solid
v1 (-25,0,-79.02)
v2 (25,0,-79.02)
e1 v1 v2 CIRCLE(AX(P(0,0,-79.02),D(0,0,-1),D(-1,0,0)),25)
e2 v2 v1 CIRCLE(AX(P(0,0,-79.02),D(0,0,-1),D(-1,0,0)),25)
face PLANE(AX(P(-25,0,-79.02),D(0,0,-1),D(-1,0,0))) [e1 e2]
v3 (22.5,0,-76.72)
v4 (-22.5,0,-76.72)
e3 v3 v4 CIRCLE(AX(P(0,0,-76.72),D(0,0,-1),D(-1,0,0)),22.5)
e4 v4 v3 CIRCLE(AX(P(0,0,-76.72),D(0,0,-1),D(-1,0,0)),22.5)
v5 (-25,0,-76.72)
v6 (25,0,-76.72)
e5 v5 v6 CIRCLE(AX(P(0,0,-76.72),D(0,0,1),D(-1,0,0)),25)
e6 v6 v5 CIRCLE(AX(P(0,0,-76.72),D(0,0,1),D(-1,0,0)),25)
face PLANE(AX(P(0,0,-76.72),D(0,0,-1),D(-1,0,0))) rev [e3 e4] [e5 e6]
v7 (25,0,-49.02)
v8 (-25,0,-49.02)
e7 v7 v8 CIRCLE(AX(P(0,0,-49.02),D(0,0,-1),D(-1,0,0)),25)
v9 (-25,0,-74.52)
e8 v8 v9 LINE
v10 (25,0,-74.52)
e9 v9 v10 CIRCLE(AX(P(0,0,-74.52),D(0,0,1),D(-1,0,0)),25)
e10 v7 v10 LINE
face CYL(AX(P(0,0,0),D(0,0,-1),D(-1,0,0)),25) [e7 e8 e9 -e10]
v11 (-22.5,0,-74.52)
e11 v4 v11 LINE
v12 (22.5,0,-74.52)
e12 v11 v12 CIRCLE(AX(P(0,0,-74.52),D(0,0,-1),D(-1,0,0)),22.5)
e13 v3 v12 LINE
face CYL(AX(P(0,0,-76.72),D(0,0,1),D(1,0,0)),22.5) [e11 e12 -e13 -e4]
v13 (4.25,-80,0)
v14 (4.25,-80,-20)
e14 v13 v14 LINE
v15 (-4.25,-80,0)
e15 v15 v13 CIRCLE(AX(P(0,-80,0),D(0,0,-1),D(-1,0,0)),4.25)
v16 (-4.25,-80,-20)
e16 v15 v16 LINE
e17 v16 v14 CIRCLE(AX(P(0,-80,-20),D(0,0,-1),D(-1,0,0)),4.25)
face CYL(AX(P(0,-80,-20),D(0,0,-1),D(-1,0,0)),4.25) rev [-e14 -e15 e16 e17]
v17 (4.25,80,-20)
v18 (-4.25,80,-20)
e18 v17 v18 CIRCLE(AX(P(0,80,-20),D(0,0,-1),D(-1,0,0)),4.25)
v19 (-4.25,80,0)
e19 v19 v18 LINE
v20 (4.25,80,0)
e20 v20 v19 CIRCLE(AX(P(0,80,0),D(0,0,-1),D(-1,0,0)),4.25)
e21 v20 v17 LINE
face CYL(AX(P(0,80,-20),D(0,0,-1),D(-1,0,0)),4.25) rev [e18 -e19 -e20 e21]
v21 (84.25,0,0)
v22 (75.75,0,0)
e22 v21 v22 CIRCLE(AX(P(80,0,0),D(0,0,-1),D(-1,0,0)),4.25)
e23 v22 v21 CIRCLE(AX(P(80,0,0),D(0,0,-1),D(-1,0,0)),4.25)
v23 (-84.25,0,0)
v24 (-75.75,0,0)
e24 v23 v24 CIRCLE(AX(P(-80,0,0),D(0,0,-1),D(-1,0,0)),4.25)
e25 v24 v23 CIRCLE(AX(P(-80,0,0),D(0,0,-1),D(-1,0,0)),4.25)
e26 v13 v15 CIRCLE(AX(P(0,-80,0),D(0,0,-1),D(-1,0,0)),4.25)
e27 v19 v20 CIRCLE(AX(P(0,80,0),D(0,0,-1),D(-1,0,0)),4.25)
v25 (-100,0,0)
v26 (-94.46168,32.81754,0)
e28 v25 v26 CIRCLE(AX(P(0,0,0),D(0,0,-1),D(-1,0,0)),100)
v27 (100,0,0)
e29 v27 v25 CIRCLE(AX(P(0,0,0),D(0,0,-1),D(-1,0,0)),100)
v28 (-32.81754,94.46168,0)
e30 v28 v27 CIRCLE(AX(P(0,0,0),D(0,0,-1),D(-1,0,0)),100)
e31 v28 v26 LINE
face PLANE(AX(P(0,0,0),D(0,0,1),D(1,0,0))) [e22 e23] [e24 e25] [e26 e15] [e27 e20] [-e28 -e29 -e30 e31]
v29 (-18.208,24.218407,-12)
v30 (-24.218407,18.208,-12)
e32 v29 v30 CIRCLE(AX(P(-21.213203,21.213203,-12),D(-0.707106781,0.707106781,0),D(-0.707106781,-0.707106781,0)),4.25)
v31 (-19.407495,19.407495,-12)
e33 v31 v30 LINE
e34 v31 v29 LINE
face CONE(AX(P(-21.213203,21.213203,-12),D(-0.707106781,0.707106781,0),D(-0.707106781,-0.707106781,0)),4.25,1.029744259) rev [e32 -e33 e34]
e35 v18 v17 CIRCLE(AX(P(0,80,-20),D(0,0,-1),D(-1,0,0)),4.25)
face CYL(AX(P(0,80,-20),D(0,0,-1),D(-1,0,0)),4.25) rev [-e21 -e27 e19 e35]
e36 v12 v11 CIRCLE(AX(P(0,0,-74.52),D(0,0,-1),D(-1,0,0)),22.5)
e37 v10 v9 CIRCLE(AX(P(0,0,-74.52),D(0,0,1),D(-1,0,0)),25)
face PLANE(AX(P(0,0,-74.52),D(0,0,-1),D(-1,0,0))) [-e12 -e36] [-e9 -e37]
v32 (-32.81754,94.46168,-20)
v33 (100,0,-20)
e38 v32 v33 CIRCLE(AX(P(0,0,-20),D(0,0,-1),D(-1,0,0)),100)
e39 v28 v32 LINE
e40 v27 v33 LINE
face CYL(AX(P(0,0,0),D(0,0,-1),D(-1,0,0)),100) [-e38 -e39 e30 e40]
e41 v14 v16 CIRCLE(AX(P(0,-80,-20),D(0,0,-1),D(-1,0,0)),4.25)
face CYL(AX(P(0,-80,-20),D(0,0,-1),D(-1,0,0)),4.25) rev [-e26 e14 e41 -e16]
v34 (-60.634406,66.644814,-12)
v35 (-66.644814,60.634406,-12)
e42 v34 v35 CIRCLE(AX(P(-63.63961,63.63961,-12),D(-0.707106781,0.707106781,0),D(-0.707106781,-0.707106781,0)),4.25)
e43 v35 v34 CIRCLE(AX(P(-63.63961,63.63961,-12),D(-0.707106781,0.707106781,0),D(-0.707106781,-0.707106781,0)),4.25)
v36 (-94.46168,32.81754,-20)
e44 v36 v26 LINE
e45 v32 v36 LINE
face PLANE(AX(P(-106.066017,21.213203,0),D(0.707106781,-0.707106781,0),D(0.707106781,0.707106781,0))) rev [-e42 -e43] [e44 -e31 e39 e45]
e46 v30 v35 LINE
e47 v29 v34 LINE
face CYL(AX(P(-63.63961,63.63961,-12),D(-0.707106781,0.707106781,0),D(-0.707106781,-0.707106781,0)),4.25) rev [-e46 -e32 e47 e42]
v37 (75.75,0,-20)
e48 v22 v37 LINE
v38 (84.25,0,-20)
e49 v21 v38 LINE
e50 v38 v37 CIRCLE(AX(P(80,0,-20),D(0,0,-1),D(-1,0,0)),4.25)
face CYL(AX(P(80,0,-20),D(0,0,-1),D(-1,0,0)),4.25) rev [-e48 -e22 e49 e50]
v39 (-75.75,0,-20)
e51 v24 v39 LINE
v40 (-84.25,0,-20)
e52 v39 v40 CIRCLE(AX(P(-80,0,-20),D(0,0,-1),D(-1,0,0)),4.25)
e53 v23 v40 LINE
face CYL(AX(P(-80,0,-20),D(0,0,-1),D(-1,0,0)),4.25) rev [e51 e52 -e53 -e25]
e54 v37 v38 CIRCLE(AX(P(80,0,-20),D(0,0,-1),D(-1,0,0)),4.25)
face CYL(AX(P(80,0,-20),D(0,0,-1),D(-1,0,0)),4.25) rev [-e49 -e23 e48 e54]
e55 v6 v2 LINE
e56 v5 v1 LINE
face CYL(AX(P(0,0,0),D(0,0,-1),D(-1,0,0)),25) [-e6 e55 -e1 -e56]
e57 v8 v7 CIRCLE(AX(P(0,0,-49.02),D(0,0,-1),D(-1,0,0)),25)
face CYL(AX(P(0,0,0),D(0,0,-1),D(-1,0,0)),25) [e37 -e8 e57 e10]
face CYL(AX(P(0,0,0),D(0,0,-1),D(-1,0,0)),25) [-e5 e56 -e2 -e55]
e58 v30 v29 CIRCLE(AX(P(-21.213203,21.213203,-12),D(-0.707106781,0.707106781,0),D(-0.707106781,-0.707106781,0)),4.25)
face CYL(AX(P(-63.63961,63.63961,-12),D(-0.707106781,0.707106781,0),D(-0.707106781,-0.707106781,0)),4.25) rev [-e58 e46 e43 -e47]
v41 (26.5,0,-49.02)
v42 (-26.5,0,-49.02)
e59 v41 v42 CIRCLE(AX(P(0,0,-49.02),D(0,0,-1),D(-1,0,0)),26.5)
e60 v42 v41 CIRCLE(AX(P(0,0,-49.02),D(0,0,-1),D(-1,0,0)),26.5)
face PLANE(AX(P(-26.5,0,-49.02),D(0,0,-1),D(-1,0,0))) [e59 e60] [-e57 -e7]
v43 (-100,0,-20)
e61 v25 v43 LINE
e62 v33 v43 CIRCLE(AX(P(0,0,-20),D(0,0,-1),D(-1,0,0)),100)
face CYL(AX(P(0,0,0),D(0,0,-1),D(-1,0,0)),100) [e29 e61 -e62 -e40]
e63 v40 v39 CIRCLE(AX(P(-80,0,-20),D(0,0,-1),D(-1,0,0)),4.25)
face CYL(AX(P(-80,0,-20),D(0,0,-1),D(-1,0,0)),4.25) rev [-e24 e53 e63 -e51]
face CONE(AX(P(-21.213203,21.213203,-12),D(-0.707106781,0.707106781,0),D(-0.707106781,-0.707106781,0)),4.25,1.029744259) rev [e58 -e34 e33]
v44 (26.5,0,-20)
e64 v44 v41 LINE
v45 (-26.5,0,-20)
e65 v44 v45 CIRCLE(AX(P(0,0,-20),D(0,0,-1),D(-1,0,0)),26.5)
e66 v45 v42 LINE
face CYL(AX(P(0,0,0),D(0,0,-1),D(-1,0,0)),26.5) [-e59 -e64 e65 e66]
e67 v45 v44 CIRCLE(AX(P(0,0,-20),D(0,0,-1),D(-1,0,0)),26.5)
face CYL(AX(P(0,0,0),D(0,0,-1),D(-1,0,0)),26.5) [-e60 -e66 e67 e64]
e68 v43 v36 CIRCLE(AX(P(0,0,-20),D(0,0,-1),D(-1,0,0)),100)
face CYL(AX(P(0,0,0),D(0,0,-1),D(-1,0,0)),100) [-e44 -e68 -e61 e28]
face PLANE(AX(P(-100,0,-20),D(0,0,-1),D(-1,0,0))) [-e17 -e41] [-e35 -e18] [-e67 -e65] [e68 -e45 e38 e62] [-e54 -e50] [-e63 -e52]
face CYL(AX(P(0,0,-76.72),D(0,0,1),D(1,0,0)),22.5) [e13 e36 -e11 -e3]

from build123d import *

# Parameters (mm, degrees)
SKETCH_4_OUTSIDE_W       = 260.734
SKETCH_4_OUTSIDE_H       = 260.734
SKETCH_4_OUTSIDE_R       = 22.5
CUT_EXTRUDE_2_DEPTH      = 2.2
HOLE_WIZARD_M10_1_D      = 8.5
PATTERN_CIRCULAR_1_COUNT = 4
CUT_EXTRUDE_5_DEPTH      = 154.242815166
HOLE_WIZARD_M10_2_D      = 8.5
HOLE_WIZARD_M10_2_DEPTH  = 60
HOLE_WIZARD_M10_2_TIP    = 2.553657631


with BuildPart() as part:
    # 草图1 → 旋转1 (revolve)
    with BuildSketch(Plane(origin=(0, 0, 0), x_dir=(1, 0, 0), z_dir=(0, 1, 0))):
        Polygon((0, 0), (-100, 0), (-100, 20), (-26.5, 20), (-26.5, 49.02), (-25, 49.02), (-25, 79.02), (0, 79.02), align=None)
    revolve(axis=Axis((0, 0, 0), (0, 0, 1)))

    # 草图4 outside → 切除-拉伸2 (cut)
    with BuildSketch(Plane(origin=(0, 0, -74.52), x_dir=(-1, 0, 0), z_dir=(0, 0, -1))):
        Rectangle(SKETCH_4_OUTSIDE_W, SKETCH_4_OUTSIDE_H)
        Circle(SKETCH_4_OUTSIDE_R, mode=Mode.SUBTRACT)
    extrude(amount=CUT_EXTRUDE_2_DEPTH, mode=Mode.SUBTRACT)

    # M10 螺纹孔1 (through all)
    with Locations(Plane(origin=(0, 0, -20), x_dir=(-1, 0, 0), z_dir=(0, 0, -1))):
        with Locations((0, -80)):
            hole_wizard_m10_1 = Hole(HOLE_WIZARD_M10_1_D / 2)

    # 阵列(圆周)1: M10 螺纹孔1 ×4 about axis
    pattern_circular_1_axis = Axis((0, 0, 0), (0, 0, 1))
    for i in range(1, PATTERN_CIRCULAR_1_COUNT):
        add(hole_wizard_m10_1.rotate(pattern_circular_1_axis, i * 360 / PATTERN_CIRCULAR_1_COUNT), mode=Mode.SUBTRACT)

    # 草图10 → 切除-拉伸5 (cut, through all)
    with BuildSketch(Plane(origin=(0, 0, -20), x_dir=(-1, 0, 0), z_dir=(0, 0, -1))):
        Polygon((106.066017178, 21.213203436), (21.213203436, 106.066017178), (56.786089274, 141.638903017), (141.638903017, 56.786089274), align=None)
    extrude(amount=-CUT_EXTRUDE_5_DEPTH, mode=Mode.SUBTRACT)

    # M10 螺纹孔2
    with Locations(Plane(origin=(-63.639610307, 63.639610307, 0), x_dir=(0.7071067811865476, 0.7071067811865475, 0), z_dir=(-0.7071067811865475, 0.7071067811865476, 0))):
        with Locations((0, 12)):
            Hole(HOLE_WIZARD_M10_2_D / 2, depth=HOLE_WIZARD_M10_2_DEPTH)
            with Locations((0, 0, -(HOLE_WIZARD_M10_2_DEPTH + HOLE_WIZARD_M10_2_TIP / 2))):  # 118° drill point
                Cone(0, HOLE_WIZARD_M10_2_D / 2, HOLE_WIZARD_M10_2_TIP, mode=Mode.SUBTRACT)


solid = part.part
